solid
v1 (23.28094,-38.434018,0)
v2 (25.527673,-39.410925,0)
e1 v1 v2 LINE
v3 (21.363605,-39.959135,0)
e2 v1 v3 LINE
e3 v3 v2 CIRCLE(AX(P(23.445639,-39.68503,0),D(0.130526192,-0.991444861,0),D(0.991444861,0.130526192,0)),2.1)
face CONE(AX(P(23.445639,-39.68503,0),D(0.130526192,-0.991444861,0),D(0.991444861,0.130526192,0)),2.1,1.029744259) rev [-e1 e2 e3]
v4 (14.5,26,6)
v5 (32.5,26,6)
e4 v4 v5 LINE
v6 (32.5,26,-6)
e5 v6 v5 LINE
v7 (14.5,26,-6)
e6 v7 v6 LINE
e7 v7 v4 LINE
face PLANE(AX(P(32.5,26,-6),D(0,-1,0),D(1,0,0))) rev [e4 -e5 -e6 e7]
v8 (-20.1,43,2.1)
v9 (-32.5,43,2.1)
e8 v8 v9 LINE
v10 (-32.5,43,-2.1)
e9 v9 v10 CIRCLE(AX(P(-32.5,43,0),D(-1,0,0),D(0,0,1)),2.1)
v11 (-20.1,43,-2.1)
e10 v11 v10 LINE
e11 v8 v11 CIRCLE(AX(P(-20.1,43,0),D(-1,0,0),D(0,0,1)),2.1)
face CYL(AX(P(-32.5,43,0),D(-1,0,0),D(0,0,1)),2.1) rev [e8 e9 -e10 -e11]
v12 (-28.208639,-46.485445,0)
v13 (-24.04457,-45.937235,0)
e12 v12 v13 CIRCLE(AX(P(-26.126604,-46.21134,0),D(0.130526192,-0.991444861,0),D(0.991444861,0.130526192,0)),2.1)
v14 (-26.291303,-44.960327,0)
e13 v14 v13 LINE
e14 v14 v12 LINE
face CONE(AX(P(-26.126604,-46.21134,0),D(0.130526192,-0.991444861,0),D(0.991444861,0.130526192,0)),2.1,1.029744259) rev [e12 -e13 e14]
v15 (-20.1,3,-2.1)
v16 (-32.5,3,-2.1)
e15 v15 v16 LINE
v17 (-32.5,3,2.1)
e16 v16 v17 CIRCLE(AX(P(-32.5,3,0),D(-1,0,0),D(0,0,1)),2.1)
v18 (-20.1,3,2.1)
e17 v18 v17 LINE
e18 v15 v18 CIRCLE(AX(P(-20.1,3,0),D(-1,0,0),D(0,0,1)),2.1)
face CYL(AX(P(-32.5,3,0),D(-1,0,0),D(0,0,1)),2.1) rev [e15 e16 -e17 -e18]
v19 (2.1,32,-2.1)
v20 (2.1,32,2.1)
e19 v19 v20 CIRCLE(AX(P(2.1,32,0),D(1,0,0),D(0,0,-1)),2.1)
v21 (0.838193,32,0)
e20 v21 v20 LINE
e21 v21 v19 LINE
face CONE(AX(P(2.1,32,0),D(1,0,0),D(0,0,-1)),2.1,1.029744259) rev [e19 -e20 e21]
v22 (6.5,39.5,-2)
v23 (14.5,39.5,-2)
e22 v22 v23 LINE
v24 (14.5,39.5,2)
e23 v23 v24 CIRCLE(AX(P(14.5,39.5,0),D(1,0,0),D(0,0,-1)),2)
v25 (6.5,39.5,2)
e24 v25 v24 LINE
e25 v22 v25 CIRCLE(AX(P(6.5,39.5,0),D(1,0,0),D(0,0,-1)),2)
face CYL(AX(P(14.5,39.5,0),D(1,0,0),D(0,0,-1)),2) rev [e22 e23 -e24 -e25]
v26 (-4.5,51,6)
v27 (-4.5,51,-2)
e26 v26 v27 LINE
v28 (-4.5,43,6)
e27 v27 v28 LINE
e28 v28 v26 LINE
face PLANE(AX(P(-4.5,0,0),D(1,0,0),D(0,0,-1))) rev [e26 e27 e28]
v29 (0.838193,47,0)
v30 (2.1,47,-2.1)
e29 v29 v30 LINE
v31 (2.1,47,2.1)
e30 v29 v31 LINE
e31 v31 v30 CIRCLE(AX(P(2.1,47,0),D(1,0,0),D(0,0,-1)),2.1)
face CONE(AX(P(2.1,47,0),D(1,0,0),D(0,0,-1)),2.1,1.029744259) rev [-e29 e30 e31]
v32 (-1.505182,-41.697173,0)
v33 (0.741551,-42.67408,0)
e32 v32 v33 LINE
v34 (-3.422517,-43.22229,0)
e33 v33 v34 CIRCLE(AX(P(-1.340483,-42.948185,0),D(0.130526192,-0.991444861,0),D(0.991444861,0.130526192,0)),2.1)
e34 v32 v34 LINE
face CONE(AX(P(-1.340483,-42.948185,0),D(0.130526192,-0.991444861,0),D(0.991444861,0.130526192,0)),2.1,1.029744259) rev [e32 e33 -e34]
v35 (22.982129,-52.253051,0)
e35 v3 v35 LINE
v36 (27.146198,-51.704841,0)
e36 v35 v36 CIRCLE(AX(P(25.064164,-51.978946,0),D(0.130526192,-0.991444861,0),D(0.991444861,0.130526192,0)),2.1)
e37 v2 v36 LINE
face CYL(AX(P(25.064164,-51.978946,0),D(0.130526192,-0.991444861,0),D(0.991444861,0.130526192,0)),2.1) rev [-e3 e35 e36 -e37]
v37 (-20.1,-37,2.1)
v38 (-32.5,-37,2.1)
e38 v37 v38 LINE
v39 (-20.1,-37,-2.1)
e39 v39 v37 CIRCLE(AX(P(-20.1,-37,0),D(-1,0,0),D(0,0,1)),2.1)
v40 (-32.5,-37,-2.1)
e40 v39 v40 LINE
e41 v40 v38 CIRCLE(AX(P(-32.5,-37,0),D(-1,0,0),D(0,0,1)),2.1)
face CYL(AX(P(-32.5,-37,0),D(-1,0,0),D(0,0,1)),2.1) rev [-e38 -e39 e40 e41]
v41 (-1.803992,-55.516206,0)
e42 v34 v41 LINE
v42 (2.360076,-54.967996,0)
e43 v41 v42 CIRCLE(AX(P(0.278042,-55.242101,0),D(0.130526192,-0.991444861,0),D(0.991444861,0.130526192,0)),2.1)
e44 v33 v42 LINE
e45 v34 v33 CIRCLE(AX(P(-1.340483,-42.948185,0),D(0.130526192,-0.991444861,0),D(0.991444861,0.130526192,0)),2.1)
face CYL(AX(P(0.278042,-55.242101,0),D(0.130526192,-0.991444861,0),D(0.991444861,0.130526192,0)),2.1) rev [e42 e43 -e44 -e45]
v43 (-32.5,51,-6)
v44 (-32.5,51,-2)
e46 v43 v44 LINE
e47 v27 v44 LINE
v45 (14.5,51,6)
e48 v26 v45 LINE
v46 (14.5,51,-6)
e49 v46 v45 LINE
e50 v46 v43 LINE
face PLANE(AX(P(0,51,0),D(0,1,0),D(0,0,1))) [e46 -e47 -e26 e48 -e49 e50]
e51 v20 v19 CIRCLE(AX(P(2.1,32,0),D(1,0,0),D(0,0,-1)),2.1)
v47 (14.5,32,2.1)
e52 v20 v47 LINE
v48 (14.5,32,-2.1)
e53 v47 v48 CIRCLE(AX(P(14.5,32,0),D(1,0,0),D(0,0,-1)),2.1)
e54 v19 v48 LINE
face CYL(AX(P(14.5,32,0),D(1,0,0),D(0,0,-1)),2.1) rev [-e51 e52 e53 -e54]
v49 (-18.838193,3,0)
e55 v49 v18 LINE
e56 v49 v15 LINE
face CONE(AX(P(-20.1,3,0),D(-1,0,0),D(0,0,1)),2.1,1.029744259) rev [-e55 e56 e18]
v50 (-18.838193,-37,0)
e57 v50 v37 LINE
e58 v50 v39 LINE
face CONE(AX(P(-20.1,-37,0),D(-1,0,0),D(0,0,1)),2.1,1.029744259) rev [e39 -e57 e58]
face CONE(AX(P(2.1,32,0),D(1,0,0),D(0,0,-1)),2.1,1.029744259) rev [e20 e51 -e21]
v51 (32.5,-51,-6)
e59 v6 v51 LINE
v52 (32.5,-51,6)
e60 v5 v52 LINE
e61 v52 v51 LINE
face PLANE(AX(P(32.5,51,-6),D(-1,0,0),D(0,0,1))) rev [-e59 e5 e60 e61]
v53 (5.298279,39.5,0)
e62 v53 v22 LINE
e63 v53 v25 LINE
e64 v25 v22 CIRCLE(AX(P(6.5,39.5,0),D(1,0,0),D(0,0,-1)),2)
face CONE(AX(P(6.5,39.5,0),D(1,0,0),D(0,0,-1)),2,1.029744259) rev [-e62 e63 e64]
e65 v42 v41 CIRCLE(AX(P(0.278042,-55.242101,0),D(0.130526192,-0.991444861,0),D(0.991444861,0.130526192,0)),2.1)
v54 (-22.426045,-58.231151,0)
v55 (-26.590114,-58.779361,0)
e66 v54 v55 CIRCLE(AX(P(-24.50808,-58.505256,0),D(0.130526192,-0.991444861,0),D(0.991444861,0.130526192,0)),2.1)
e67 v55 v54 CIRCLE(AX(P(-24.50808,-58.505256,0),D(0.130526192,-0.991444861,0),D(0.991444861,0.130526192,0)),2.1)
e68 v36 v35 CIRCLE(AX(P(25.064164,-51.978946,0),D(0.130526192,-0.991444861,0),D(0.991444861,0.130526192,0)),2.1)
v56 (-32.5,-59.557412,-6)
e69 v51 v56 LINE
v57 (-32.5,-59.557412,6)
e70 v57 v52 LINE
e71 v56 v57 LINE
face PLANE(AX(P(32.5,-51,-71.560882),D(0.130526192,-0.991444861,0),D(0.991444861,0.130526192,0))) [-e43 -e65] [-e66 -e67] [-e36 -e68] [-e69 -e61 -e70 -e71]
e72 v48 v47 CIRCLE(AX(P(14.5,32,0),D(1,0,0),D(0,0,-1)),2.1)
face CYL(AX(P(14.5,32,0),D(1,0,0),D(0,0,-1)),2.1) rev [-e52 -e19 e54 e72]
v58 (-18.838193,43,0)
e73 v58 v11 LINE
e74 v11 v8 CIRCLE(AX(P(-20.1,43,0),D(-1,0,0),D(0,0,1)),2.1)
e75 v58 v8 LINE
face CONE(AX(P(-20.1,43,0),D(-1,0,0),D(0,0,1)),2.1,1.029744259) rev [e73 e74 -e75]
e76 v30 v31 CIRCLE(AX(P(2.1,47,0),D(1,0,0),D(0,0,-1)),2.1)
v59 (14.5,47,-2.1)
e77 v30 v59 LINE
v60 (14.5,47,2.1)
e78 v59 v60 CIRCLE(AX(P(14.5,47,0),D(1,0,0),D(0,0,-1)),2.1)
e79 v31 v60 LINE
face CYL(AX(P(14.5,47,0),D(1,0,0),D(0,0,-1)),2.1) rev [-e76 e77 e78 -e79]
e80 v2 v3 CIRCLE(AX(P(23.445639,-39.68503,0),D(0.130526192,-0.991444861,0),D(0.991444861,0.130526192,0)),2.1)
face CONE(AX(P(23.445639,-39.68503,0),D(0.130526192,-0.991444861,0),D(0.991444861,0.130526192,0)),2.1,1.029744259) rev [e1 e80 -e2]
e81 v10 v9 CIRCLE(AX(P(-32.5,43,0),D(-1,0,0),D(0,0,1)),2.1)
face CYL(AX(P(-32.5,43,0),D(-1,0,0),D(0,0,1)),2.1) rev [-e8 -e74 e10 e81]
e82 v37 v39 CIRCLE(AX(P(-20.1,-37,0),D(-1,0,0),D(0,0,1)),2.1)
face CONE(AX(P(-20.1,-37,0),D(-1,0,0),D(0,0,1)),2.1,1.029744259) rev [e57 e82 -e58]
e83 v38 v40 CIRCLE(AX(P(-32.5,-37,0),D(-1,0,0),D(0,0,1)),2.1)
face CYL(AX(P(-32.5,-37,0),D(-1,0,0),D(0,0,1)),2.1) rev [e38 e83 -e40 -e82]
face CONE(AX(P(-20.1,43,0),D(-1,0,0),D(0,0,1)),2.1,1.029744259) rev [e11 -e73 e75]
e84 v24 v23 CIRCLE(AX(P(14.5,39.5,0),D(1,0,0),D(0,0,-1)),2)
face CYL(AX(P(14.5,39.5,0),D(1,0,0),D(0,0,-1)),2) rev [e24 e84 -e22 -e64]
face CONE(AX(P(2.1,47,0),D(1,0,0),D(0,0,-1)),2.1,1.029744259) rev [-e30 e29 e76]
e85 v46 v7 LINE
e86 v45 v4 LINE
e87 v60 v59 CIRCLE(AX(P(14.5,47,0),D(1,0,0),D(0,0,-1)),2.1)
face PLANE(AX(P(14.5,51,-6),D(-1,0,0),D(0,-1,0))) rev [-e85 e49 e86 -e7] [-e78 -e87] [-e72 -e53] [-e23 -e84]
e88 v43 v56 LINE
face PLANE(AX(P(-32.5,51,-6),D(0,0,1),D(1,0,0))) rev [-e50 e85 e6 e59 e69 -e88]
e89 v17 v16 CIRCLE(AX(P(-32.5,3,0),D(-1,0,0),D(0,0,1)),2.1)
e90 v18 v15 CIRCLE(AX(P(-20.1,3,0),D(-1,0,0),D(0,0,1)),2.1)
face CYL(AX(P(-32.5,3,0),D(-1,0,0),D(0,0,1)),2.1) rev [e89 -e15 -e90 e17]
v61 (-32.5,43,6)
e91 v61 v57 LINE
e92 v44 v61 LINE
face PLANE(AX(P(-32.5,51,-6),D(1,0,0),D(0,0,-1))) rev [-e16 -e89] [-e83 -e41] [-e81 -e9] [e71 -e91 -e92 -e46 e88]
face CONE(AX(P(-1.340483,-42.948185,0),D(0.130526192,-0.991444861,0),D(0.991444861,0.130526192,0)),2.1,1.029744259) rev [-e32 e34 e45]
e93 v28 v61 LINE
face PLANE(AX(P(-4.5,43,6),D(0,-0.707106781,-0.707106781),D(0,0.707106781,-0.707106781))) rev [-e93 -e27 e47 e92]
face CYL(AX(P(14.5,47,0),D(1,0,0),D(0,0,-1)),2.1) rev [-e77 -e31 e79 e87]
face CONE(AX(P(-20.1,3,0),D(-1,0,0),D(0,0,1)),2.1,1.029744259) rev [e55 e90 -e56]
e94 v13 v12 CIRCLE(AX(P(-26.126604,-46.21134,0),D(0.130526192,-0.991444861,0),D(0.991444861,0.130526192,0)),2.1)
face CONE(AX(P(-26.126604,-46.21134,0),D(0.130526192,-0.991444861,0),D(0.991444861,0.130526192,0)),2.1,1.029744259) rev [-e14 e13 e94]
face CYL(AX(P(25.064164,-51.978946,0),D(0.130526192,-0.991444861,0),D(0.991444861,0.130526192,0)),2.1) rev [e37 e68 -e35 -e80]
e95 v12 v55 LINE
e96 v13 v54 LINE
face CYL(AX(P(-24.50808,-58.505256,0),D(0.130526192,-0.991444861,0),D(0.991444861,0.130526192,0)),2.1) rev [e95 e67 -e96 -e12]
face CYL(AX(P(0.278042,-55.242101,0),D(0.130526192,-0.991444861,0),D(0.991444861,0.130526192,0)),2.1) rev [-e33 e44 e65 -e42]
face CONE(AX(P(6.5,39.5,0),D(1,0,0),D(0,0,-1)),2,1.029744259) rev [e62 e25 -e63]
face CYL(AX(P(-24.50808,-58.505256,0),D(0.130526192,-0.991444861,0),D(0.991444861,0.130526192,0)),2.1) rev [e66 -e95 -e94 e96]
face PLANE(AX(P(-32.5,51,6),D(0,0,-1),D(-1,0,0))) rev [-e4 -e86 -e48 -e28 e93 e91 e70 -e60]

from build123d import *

# Parameters (mm, degrees)
SKETCH1_W                    = 65
SKETCH1_H                    = 12
BOSS_EXTRUDE1_DEPTH          = 51
BOSS_EXTRUDE2_DEPTH          = 12
SKETCH3_W                    = 18
SKETCH3_H                    = 25
CUT_EXTRUDE2_DEPTH           = 69.900909755
M5_TAPPED_HOLE1_D            = 4.2
M5_TAPPED_HOLE1_DEPTH        = 12.4
M5_TAPPED_HOLE1_TIP          = 1.2618073
M5_TAPPED_HOLE2_D            = 4.2
M5_TAPPED_HOLE2_DEPTH        = 12.4
M5_TAPPED_HOLE2_TIP          = 1.2618073
M5_TAPPED_HOLE3_D            = 4.2
M5_TAPPED_HOLE3_DEPTH        = 12.4
M5_TAPPED_HOLE3_TIP          = 1.2618073
CUT_EXTRUDE3_DEPTH           = 28
F_4_0_4_DIAMETER_HOLE1_D     = 4
F_4_0_4_DIAMETER_HOLE1_DEPTH = 8
F_4_0_4_DIAMETER_HOLE1_TIP   = 1.201721238


with BuildPart() as part:
    # Sketch1 → Boss-Extrude1 (new, symmetric)
    with BuildSketch(Plane(origin=(0, 0, 0), x_dir=(1, 0, 0), z_dir=(0, 1, 0))):
        Rectangle(SKETCH1_W, SKETCH1_H)
    extrude(amount=BOSS_EXTRUDE1_DEPTH, both=True)

    # Sketch4 → Boss-Extrude2 (add)
    with BuildSketch(Plane.XY.offset(6)):
        Polygon((-32.5, -51), (32.5, -51), (-32.5, -59.557412343), align=None)
    extrude(amount=-BOSS_EXTRUDE2_DEPTH)

    # Sketch3 → Cut-Extrude2 (cut, through all)
    with BuildSketch(Plane.XY.offset(6)):
        with Locations((23.5, 38.5)):
            Rectangle(SKETCH3_W, SKETCH3_H)
    extrude(amount=-CUT_EXTRUDE2_DEPTH, mode=Mode.SUBTRACT)

    # M5 Tapped Hole1
    with Locations(Plane(origin=(7.153590973, -54.336918053, 0), x_dir=(-0.9914448613738113, -0.13052619222004513, 0), z_dir=(0.13052619222004513, -0.9914448613738113, 0))):
        with Locations((-18.065122191, 0), (6.934877809, 0), (31.934877809, 0)):
            Hole(M5_TAPPED_HOLE1_D / 2, depth=M5_TAPPED_HOLE1_DEPTH)
            with Locations((0, 0, -(M5_TAPPED_HOLE1_DEPTH + M5_TAPPED_HOLE1_TIP / 2))):  # 118° drill point
                Cone(0, M5_TAPPED_HOLE1_D / 2, M5_TAPPED_HOLE1_TIP, mode=Mode.SUBTRACT)

    # M5 Tapped Hole2
    with Locations(Plane.ZY.offset(32.5)):
        with Locations((0, 43), (0, 3), (0, -37)):
            Hole(M5_TAPPED_HOLE2_D / 2, depth=M5_TAPPED_HOLE2_DEPTH)
            with Locations((0, 0, -(M5_TAPPED_HOLE2_DEPTH + M5_TAPPED_HOLE2_TIP / 2))):  # 118° drill point
                Cone(0, M5_TAPPED_HOLE2_D / 2, M5_TAPPED_HOLE2_TIP, mode=Mode.SUBTRACT)

    # M5 Tapped Hole3
    with Locations(Plane(origin=(14.5, 0, 0), x_dir=(0, 0, -1), z_dir=(1, 0, 0))):
        with Locations((0, 47), (0, 32)):
            Hole(M5_TAPPED_HOLE3_D / 2, depth=M5_TAPPED_HOLE3_DEPTH)
            with Locations((0, 0, -(M5_TAPPED_HOLE3_DEPTH + M5_TAPPED_HOLE3_TIP / 2))):  # 118° drill point
                Cone(0, M5_TAPPED_HOLE3_D / 2, M5_TAPPED_HOLE3_TIP, mode=Mode.SUBTRACT)

    # Sketch12 → Cut-Extrude3 (cut)
    with BuildSketch(Plane.ZY.offset(32.5)):
        Polygon((-2, 51), (6, 51), (6, 43), align=None)
    extrude(amount=-CUT_EXTRUDE3_DEPTH, mode=Mode.SUBTRACT)

    # Ø4.0 (4) Diameter Hole1
    with Locations(Plane(origin=(14.5, 0, 0), x_dir=(0, 0, -1), z_dir=(1, 0, 0))):
        with Locations((0, 39.5)):
            Hole(F_4_0_4_DIAMETER_HOLE1_D / 2, depth=F_4_0_4_DIAMETER_HOLE1_DEPTH)
            with Locations((0, 0, -(F_4_0_4_DIAMETER_HOLE1_DEPTH + F_4_0_4_DIAMETER_HOLE1_TIP / 2))):  # 118° drill point
                Cone(0, F_4_0_4_DIAMETER_HOLE1_D / 2, F_4_0_4_DIAMETER_HOLE1_TIP, mode=Mode.SUBTRACT)


solid = part.part
